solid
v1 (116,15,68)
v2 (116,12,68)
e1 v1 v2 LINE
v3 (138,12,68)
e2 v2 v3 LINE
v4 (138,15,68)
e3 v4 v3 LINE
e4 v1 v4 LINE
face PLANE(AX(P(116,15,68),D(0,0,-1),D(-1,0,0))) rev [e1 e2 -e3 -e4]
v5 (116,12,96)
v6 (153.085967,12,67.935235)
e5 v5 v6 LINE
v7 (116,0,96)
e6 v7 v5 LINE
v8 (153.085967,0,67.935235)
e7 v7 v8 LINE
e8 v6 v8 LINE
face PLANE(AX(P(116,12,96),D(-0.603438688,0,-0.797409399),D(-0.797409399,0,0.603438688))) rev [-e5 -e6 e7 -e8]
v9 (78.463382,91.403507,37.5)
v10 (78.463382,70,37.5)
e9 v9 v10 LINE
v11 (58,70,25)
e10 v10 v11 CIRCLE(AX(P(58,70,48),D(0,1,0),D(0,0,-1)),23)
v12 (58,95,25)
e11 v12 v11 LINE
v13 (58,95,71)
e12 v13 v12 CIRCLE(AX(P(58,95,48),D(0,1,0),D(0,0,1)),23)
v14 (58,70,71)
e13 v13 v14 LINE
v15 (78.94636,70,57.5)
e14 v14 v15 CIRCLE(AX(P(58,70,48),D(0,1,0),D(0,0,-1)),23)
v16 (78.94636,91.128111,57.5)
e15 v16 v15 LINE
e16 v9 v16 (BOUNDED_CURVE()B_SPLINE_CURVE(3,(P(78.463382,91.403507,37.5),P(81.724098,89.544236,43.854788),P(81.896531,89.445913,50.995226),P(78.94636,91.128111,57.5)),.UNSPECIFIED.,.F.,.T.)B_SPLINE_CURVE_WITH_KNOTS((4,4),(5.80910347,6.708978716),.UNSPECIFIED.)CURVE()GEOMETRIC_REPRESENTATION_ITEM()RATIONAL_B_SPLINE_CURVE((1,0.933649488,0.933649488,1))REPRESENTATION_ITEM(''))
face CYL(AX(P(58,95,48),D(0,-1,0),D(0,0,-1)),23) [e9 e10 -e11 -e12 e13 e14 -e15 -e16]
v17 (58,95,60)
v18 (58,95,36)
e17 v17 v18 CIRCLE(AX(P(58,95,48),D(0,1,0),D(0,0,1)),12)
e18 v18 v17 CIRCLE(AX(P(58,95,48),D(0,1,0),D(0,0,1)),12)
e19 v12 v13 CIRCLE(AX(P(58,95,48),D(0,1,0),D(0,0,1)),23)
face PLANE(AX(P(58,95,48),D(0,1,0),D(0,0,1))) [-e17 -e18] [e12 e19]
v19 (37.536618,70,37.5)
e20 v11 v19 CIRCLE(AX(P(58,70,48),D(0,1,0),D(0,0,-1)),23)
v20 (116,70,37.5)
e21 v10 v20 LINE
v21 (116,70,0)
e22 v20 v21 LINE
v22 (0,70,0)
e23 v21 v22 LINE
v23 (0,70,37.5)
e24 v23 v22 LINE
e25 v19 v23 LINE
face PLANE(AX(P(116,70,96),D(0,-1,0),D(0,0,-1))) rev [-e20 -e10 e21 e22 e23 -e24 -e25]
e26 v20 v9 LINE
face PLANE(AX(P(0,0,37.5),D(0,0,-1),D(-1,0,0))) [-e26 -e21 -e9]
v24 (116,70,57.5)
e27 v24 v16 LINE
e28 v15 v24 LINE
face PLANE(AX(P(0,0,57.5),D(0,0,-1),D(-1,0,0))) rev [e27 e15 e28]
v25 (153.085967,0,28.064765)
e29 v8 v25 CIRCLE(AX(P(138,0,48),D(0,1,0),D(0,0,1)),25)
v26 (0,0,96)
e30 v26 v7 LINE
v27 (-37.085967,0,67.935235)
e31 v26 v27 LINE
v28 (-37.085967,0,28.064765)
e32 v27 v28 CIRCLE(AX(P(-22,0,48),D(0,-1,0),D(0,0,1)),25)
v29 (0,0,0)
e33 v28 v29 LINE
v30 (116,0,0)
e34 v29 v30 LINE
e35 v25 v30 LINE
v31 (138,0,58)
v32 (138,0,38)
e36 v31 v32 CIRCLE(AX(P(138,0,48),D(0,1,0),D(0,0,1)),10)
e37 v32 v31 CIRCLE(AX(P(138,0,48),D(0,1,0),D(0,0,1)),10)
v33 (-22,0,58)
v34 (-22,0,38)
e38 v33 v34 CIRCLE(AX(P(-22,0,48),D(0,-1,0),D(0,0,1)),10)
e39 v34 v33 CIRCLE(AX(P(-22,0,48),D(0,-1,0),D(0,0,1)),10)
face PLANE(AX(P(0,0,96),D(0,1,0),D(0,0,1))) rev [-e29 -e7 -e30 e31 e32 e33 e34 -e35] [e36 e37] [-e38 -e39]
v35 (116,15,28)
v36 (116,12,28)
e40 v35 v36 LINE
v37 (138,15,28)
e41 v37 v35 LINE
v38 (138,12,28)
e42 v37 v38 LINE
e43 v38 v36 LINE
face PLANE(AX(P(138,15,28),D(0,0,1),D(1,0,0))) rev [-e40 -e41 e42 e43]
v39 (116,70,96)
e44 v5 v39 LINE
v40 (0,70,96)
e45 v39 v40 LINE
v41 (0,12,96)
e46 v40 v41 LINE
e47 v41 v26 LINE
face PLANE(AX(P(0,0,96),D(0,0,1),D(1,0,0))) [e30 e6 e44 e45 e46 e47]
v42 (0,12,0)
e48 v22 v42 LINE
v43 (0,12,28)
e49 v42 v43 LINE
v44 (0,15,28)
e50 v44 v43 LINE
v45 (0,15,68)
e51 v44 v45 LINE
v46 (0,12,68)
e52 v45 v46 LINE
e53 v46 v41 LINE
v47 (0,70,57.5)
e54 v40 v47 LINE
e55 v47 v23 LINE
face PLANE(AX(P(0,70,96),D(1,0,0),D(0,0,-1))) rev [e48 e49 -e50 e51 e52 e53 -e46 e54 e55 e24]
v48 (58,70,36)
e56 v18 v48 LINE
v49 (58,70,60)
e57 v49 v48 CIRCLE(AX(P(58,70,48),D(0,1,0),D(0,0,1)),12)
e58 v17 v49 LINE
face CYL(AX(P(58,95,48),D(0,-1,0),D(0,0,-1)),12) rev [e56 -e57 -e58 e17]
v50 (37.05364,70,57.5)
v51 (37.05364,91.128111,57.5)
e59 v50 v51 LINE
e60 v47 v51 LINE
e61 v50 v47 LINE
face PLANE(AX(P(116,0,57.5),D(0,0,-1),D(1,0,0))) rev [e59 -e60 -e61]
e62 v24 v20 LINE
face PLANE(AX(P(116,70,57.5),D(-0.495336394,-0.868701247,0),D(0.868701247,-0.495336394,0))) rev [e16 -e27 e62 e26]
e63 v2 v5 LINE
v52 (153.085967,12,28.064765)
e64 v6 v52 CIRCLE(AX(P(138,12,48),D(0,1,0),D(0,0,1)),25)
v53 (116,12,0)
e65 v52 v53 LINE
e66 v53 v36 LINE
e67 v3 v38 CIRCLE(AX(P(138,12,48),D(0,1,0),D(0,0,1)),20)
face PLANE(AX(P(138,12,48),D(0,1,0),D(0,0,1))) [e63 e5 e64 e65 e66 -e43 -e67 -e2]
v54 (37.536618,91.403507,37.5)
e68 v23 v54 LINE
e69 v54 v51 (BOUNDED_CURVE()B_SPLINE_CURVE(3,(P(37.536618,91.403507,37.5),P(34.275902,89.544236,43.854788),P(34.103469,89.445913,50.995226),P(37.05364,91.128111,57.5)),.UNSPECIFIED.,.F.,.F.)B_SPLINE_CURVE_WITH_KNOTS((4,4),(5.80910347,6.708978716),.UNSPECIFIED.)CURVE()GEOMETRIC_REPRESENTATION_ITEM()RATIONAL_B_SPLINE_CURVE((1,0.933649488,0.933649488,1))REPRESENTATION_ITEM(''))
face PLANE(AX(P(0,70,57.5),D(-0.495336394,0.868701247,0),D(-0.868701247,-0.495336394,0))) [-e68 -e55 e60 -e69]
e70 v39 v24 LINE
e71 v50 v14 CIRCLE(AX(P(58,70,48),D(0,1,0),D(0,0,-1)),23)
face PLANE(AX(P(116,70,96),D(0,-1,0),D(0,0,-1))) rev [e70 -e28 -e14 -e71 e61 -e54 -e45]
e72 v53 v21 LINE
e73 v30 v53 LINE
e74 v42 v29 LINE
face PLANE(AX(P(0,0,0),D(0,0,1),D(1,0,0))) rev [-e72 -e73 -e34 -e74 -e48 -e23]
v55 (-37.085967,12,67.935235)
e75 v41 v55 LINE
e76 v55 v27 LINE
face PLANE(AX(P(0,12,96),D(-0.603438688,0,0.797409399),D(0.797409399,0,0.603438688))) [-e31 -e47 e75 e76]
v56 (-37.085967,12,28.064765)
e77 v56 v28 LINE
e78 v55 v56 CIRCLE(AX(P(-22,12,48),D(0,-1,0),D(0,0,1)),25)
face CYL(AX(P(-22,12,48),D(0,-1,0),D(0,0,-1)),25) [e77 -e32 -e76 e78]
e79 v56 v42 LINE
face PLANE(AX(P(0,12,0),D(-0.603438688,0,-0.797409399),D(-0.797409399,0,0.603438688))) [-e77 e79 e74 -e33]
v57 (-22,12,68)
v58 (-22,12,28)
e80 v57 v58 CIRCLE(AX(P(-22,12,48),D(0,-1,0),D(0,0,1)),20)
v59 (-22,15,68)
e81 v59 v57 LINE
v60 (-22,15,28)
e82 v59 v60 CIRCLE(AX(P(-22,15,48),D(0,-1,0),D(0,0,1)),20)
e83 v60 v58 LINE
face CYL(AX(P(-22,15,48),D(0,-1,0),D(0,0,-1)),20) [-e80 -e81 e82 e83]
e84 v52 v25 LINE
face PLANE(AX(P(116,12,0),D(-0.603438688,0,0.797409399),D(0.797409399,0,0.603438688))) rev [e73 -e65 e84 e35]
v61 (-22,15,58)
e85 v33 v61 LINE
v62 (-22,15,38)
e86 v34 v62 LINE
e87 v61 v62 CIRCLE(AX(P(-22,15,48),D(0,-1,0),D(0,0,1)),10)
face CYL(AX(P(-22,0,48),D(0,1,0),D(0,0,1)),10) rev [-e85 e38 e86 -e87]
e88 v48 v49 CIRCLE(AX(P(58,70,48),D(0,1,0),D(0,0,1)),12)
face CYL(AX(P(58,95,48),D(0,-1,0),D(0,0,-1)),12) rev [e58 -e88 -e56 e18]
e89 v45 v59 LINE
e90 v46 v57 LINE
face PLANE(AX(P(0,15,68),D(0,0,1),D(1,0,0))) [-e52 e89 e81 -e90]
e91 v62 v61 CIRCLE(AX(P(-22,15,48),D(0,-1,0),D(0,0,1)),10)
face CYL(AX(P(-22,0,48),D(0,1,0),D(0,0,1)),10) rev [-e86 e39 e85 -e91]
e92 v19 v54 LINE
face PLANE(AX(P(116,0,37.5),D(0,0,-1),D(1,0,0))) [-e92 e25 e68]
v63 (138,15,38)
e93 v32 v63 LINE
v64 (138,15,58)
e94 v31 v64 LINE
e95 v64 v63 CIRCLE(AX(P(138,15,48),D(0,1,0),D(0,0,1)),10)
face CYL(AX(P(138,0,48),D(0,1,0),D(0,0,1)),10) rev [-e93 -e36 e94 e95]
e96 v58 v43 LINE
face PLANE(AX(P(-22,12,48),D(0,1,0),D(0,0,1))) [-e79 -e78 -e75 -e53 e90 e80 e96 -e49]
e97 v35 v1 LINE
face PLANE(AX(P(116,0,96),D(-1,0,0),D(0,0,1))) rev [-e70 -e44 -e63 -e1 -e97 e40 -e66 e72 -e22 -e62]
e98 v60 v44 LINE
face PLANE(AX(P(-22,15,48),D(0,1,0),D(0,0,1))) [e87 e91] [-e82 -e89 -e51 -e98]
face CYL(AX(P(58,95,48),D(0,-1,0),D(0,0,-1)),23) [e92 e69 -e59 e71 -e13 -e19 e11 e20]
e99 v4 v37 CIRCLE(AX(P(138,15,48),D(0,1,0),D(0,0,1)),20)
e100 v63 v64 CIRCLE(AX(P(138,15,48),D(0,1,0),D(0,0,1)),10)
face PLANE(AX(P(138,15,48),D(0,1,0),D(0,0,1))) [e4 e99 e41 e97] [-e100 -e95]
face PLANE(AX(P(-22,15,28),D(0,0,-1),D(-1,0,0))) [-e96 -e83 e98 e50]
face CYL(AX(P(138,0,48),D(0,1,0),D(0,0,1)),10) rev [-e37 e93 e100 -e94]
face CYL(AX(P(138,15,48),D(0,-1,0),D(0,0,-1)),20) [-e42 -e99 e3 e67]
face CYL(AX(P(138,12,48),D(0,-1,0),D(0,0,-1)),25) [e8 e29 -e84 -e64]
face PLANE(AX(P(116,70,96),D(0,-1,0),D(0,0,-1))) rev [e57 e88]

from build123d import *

# Parameters (mm, degrees)
HOUSING_BLOCK_SKETCH_W = 116
HOUSING_BLOCK_SKETCH_H = 70
HOUSING_BLOCK_DEPTH    = 96
MOUNTING_FLANGE_DEPTH  = 12
FLANGE_PAD_DEPTH       = 3
FLANGE_HOLE_SKETCH_R   = 10
FLANGE_HOLE_DEPTH      = 198.002538055
TOP_BOSS_SKETCH_R      = 23
TOP_BOSS_SKETCH_R_2    = 12
TOP_BOSS_46_DEPTH      = 25
GUSSET_DEPTH           = 10


with BuildPart() as part:
    # Housing Block Sketch → Housing Block (new body)
    with BuildSketch(Plane.XY):
        with Locations((58, 35)):
            Rectangle(HOUSING_BLOCK_SKETCH_W, HOUSING_BLOCK_SKETCH_H)
    extrude(amount=HOUSING_BLOCK_DEPTH)

    # Mounting Flange Sketch → Mounting Flange (add)
    with BuildSketch(Plane(origin=(0, 0, 0), x_dir=(1, 0, 0), z_dir=(0, 1, 0))):
        with BuildLine():
            Line((116, 0), (116, -96))
            Line((116, -96), (153.08596721, -67.935234971))
            ThreePointArc((153.08596721, -67.935234971), (163, -48), (153.08596721, -28.064765029))
            Line((153.08596721, -28.064765029), (116, 0))
        make_face()
    mounting_flange = extrude(amount=MOUNTING_FLANGE_DEPTH)

    # Flange Pad Sketch → Flange Pad (add)
    with BuildSketch(Plane(origin=(0, 12, 0), x_dir=(1, 0, 0), z_dir=(0, 1, 0))):
        with BuildLine():
            Line((138, -28), (116, -28))
            Line((116, -28), (116, -68))
            Line((116, -68), (138, -68))
            ThreePointArc((138, -68), (158, -48), (138, -28))
        make_face()
    flange_pad = extrude(amount=FLANGE_PAD_DEPTH)

    # Flange Hole Sketch → Flange Hole (cut, through all)
    with BuildSketch(Plane(origin=(0, 15, 0), x_dir=(1, 0, 0), z_dir=(0, 1, 0))):
        with Locations(Location((138, -48, 0), (0, 0, 270))):
            Circle(FLANGE_HOLE_SKETCH_R)
    flange_hole = extrude(amount=-FLANGE_HOLE_DEPTH, mode=Mode.SUBTRACT)

    # Flange Mirror: Mounting Flange, Flange Pad, Flange Hole across plane
    add(mounting_flange.mirror(Plane(origin=(58, 0, 0), x_dir=(0, 0, 1), z_dir=(1, 0, 0))))
    add(flange_pad.mirror(Plane(origin=(58, 0, 0), x_dir=(0, 0, 1), z_dir=(1, 0, 0))))
    add(flange_hole.mirror(Plane(origin=(58, 0, 0), x_dir=(0, 0, 1), z_dir=(1, 0, 0))), mode=Mode.SUBTRACT)

    # Top Boss Sketch → Top Boss Ø46 (add)
    with BuildSketch(Plane(origin=(0, 70, 0), x_dir=(1, 0, 0), z_dir=(0, 1, 0))):
        with Locations(Location((58, -48, 0), (0, 0, 90))):
            Circle(TOP_BOSS_SKETCH_R)
        with Locations(Location((58, -48, 0), (0, 0, 270))):
            Circle(TOP_BOSS_SKETCH_R_2, mode=Mode.SUBTRACT)
    extrude(amount=TOP_BOSS_46_DEPTH)

    # Gusset Sketch → Gusset (add, symmetric)
    with BuildSketch(Plane.XY.offset(47.5)):
        Polygon((81, 70), (116, 70), (72.155995343, 95), (72.155995343, 70), align=None)
    gusset = extrude(amount=GUSSET_DEPTH, both=True)

    # Gusset Mirror: Gusset across plane
    add(gusset.mirror(Plane(origin=(58, 0, 0), x_dir=(0, 0, 1), z_dir=(1, 0, 0))))


solid = part.part
